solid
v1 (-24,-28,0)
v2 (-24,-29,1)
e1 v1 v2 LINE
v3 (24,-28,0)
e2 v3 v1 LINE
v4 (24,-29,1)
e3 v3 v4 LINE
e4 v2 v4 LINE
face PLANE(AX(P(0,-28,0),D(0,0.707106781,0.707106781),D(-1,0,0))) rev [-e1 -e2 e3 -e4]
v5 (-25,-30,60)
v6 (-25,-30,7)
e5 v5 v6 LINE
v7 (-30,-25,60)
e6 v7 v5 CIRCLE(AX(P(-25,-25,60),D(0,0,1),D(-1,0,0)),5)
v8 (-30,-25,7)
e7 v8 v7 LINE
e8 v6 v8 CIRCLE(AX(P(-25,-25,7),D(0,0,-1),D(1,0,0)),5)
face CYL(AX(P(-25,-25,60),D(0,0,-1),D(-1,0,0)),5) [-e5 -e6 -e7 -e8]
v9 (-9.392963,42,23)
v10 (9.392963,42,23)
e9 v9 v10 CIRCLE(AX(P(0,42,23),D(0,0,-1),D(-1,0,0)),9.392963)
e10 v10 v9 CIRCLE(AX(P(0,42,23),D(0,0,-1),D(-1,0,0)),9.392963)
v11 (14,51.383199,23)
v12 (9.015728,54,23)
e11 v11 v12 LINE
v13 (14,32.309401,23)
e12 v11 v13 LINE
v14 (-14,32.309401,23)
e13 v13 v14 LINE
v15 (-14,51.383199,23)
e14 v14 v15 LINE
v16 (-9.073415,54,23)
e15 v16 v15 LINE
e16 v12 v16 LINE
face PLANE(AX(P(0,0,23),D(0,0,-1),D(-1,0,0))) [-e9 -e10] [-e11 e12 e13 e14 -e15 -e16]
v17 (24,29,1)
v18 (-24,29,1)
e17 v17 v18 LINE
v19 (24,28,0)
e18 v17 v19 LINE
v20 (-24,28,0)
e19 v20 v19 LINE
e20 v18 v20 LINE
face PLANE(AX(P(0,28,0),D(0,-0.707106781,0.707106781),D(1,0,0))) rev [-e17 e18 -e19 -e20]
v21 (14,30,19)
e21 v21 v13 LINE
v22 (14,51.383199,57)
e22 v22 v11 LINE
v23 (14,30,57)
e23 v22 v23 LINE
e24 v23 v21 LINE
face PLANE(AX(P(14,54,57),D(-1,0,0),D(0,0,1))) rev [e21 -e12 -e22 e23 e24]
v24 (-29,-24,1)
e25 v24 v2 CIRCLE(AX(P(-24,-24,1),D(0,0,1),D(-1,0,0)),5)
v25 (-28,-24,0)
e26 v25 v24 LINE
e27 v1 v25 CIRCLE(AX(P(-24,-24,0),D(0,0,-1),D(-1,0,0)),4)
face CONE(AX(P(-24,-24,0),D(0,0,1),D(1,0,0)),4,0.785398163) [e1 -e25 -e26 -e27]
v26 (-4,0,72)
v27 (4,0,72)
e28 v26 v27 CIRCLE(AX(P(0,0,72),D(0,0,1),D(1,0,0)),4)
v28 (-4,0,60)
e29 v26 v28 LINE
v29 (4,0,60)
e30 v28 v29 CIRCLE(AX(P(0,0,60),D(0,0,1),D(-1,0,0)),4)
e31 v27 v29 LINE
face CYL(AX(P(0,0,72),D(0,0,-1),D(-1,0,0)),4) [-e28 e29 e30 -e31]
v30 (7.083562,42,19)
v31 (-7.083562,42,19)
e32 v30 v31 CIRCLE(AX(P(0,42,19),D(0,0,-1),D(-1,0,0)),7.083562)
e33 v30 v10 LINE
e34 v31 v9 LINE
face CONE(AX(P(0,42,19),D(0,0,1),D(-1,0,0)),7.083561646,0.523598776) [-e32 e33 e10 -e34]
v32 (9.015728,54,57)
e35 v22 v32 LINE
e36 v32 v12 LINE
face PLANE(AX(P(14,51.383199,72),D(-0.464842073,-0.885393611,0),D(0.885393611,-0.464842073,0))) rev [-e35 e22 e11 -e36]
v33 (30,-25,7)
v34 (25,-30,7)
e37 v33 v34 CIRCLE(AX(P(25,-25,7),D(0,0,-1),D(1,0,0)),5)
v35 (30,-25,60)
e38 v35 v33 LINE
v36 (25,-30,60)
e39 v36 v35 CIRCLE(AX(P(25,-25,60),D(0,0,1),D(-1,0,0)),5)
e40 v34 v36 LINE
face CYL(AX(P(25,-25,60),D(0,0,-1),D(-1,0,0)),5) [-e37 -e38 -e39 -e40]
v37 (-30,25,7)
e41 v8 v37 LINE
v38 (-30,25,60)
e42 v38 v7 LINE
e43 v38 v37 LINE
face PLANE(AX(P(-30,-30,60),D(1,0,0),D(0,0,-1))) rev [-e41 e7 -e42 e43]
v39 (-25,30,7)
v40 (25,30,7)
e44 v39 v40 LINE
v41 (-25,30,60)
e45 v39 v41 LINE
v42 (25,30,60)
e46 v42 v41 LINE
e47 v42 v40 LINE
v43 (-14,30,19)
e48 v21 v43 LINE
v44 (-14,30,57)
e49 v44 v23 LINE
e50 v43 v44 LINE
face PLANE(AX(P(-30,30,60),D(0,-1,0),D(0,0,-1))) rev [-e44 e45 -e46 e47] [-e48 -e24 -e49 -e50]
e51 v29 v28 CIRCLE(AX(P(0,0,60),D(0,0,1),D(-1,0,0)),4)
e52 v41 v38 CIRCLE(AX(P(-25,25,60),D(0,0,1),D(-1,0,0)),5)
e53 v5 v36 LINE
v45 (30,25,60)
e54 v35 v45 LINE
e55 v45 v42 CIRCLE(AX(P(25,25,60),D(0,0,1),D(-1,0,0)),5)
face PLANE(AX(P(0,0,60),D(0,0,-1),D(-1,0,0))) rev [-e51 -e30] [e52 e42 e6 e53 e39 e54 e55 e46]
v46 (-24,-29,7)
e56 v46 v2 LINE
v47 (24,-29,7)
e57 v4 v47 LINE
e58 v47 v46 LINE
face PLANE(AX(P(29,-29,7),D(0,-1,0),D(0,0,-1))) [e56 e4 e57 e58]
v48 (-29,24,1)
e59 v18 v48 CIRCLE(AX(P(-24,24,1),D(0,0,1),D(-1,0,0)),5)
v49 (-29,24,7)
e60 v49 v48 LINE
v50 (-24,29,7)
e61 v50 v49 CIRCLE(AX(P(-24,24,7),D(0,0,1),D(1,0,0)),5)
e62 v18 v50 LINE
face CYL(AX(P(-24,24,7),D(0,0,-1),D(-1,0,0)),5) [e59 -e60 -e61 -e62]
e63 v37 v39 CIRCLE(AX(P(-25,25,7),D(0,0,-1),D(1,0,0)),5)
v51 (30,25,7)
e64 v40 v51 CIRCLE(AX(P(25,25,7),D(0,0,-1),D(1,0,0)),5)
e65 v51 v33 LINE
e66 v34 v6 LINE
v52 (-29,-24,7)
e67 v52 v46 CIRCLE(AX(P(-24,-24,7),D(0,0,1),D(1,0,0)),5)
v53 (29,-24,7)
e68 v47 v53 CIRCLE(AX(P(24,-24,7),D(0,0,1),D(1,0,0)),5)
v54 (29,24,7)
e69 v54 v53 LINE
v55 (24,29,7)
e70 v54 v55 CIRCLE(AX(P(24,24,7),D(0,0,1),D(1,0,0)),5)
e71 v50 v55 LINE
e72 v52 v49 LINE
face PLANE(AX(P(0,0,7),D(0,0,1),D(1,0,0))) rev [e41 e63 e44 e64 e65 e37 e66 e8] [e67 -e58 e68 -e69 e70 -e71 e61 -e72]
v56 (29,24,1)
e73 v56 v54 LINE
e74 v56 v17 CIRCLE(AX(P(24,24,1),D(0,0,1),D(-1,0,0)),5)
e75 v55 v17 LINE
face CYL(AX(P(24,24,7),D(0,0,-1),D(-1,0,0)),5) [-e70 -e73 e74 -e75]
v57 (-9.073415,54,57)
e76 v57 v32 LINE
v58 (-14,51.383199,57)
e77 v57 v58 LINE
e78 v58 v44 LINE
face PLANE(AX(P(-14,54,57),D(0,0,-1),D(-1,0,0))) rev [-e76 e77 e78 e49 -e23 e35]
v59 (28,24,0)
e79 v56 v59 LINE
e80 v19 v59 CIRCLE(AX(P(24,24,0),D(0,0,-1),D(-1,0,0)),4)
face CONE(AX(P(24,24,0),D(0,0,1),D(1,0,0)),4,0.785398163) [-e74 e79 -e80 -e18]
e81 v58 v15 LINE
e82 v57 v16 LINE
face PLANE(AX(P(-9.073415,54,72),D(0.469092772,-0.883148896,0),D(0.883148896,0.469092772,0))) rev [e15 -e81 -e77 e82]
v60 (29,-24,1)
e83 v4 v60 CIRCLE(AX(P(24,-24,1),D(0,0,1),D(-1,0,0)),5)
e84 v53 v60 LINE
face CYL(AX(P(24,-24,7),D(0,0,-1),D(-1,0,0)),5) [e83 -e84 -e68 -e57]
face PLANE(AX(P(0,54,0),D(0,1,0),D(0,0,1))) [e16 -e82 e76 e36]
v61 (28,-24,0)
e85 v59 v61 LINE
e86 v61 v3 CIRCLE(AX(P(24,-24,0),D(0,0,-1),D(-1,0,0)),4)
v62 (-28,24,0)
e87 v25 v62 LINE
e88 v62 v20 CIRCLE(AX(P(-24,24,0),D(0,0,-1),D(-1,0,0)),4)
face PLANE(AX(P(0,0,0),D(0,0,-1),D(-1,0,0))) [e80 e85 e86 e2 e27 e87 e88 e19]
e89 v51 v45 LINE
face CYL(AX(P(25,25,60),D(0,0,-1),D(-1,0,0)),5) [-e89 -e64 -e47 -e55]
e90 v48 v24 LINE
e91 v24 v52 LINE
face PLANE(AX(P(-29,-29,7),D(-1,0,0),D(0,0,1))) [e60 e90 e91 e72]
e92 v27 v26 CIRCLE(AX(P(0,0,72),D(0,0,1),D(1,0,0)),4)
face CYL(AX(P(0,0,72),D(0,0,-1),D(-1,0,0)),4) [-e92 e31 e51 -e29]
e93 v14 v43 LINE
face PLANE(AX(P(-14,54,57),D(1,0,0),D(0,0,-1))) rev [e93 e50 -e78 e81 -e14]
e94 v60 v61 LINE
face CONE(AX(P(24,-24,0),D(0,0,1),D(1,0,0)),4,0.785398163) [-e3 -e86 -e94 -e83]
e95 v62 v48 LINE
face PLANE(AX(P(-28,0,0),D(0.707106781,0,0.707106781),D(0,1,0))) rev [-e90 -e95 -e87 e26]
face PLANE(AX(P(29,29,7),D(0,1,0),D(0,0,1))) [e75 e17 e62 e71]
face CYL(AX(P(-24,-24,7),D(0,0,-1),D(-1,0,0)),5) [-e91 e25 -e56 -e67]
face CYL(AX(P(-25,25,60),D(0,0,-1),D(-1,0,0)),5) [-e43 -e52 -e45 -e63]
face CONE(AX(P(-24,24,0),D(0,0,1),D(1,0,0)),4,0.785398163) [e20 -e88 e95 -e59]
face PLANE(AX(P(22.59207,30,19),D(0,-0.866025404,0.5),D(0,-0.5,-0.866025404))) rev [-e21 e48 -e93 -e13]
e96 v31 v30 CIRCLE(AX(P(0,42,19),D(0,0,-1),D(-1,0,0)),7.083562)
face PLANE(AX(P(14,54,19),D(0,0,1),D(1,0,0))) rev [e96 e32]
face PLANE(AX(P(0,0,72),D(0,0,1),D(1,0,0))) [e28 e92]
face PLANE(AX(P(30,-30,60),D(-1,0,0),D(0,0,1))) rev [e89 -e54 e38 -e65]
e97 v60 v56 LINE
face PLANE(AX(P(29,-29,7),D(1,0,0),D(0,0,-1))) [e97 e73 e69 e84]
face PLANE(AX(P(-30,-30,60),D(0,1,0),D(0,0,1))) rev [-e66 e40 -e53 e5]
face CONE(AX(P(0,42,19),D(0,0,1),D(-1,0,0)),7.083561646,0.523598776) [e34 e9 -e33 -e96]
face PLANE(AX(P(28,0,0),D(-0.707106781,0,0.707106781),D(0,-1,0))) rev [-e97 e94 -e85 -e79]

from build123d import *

# Parameters (mm, degrees)
SKETCH_1_W          = 60
SKETCH_1_H          = 60
EXTRUDE_1_DEPTH     = 60
SKETCH_2_R          = 4
EXTRUDE_2_DEPTH     = 12
SKETCH_3_W          = 60
SKETCH_3_H          = 60
SKETCH_3_W_2        = 58
SKETCH_3_H_2        = 58
CUT_EXTRUDE_1_DEPTH = 7
FILLET_1_R          = 5
CHAMFER_1_SIZE      = 1
FILLET_2_R          = 5
SKETCH_5_W          = 28
SKETCH_5_H          = 38
EXTRUDE_3_DEPTH     = 24
SKETCH_6_W          = 44.228024493
SKETCH_6_H          = 29.890039758
SKETCH_6_R          = 7.083561646
CUT_EXTRUDE_2_DEPTH = 4
CUT_EXTRUDE_2_DRAFT = -30
CUT_EXTRUDE_3_DEPTH = 79.847954951


with BuildPart() as part:
    # 草图1 → 凸台-拉伸1 (new body)
    with BuildSketch(Plane.XY):
        Rectangle(SKETCH_1_W, SKETCH_1_H)
    extrude(amount=EXTRUDE_1_DEPTH)

    # 草图2 → 凸台-拉伸2 (add)
    with BuildSketch(Plane.XY.offset(60)):
        with Locations(Location((0, 0, 0), (0, 0, 180))):
            Circle(SKETCH_2_R)
    extrude(amount=EXTRUDE_2_DEPTH)

    # 草图3 → 切除-拉伸1 (cut)
    with BuildSketch(Plane(origin=(0, 0, 0), x_dir=(-1, 0, 0), z_dir=(0, 0, -1))):
        Rectangle(SKETCH_3_W, SKETCH_3_H)
        Rectangle(SKETCH_3_W_2, SKETCH_3_H_2, mode=Mode.SUBTRACT)
    extrude(amount=-CUT_EXTRUDE_1_DEPTH, mode=Mode.SUBTRACT)

    # 圆角1
    fillet_1_edges = [part.edges().sort_by_distance(p)[0] for p in [
        (-29, -29, 3.5),
        (29, -29, 3.5),
        (29, 29, 3.5),
        (-29, 29, 3.5),
    ]]
    fillet(fillet_1_edges, radius=FILLET_1_R)

    # 倒角1
    chamfer_1_edges = [part.edges().sort_by_distance(p)[0] for p in [
        (-29, 0, 0),
        (0, -29, 0),
        (0, 29, 0),
        (29, 0, 0),
        (27.535533906, 27.535533906, 0),
        (27.535533906, -27.535533906, 0),
        (-27.535533906, -27.535533906, 0),
        (-27.535533906, 27.535533906, 0),
    ]]
    chamfer(chamfer_1_edges, length=CHAMFER_1_SIZE)

    # 圆角2
    fillet_2_edges = [part.edges().sort_by_distance(p)[0] for p in [
        (30, -30, 33.5),
        (-30, -30, 33.5),
        (-30, 30, 33.5),
        (30, 30, 33.5),
    ]]
    fillet(fillet_2_edges, radius=FILLET_2_R)

    # 草图5 → 凸台-拉伸3 (add)
    with BuildSketch(Plane(origin=(0, 30, 0), x_dir=(1, 0, 0), z_dir=(0, 1, 0))):
        with Locations((0, -38)):
            Rectangle(SKETCH_5_W, SKETCH_5_H)
    extrude(amount=EXTRUDE_3_DEPTH)


with BuildPart() as cut_extrude_2_tool:
    # 草图6 → 切除-拉伸2 (with draft: the straight prism first)
    with BuildSketch(Plane(origin=(0, 0, 19), x_dir=(-1, 0, 0), z_dir=(0, 0, -1))):
        with Locations((-0.478057726, 44.945019879)):
            Rectangle(SKETCH_6_W, SKETCH_6_H)
        with Locations((0, 42)):
            Circle(SKETCH_6_R, mode=Mode.SUBTRACT)
    extrude(amount=-CUT_EXTRUDE_2_DEPTH)
    # 切除-拉伸2: the draft: its side faces are tilted about the plane it starts from
    cut_extrude_2_sides = [cut_extrude_2_tool.faces().sort_by_distance(p)[0] for p in [
        (22.592069973, 44.945019879, 21),
        (0.478057727, 30, 21),
        (-21.63595452, 44.945019879, 21),
        (0.478057727, 59.890039758, 21),
        (7.083561646, 42, 21),
    ]]
    draft(cut_extrude_2_sides, Plane(origin=(0, 0, 19), x_dir=(-1, 0, 0), z_dir=(0, 0, -1)), CUT_EXTRUDE_2_DRAFT)


with BuildPart() as part_1:
    add(part.part)

    # 切除-拉伸2: cut by cut_extrude_2_tool
    add(cut_extrude_2_tool.part, mode=Mode.SUBTRACT)

    # 草图7 → 切除-拉伸3 (cut, through all)
    with BuildSketch(Plane(origin=(0, 0, 23), x_dir=(-1, 0, 0), z_dir=(0, 0, -1))):
        Polygon((-14, 51.383198576), (-9.015728145, 54), (9.073415265, 54), (14, 51.383198576), (16.492135927, 52.691599288), (15.246067964, 56.551525264), (-18.004122386, 56.551525264), align=None)
    extrude(amount=-CUT_EXTRUDE_3_DEPTH, mode=Mode.SUBTRACT)


solid = part_1.part
